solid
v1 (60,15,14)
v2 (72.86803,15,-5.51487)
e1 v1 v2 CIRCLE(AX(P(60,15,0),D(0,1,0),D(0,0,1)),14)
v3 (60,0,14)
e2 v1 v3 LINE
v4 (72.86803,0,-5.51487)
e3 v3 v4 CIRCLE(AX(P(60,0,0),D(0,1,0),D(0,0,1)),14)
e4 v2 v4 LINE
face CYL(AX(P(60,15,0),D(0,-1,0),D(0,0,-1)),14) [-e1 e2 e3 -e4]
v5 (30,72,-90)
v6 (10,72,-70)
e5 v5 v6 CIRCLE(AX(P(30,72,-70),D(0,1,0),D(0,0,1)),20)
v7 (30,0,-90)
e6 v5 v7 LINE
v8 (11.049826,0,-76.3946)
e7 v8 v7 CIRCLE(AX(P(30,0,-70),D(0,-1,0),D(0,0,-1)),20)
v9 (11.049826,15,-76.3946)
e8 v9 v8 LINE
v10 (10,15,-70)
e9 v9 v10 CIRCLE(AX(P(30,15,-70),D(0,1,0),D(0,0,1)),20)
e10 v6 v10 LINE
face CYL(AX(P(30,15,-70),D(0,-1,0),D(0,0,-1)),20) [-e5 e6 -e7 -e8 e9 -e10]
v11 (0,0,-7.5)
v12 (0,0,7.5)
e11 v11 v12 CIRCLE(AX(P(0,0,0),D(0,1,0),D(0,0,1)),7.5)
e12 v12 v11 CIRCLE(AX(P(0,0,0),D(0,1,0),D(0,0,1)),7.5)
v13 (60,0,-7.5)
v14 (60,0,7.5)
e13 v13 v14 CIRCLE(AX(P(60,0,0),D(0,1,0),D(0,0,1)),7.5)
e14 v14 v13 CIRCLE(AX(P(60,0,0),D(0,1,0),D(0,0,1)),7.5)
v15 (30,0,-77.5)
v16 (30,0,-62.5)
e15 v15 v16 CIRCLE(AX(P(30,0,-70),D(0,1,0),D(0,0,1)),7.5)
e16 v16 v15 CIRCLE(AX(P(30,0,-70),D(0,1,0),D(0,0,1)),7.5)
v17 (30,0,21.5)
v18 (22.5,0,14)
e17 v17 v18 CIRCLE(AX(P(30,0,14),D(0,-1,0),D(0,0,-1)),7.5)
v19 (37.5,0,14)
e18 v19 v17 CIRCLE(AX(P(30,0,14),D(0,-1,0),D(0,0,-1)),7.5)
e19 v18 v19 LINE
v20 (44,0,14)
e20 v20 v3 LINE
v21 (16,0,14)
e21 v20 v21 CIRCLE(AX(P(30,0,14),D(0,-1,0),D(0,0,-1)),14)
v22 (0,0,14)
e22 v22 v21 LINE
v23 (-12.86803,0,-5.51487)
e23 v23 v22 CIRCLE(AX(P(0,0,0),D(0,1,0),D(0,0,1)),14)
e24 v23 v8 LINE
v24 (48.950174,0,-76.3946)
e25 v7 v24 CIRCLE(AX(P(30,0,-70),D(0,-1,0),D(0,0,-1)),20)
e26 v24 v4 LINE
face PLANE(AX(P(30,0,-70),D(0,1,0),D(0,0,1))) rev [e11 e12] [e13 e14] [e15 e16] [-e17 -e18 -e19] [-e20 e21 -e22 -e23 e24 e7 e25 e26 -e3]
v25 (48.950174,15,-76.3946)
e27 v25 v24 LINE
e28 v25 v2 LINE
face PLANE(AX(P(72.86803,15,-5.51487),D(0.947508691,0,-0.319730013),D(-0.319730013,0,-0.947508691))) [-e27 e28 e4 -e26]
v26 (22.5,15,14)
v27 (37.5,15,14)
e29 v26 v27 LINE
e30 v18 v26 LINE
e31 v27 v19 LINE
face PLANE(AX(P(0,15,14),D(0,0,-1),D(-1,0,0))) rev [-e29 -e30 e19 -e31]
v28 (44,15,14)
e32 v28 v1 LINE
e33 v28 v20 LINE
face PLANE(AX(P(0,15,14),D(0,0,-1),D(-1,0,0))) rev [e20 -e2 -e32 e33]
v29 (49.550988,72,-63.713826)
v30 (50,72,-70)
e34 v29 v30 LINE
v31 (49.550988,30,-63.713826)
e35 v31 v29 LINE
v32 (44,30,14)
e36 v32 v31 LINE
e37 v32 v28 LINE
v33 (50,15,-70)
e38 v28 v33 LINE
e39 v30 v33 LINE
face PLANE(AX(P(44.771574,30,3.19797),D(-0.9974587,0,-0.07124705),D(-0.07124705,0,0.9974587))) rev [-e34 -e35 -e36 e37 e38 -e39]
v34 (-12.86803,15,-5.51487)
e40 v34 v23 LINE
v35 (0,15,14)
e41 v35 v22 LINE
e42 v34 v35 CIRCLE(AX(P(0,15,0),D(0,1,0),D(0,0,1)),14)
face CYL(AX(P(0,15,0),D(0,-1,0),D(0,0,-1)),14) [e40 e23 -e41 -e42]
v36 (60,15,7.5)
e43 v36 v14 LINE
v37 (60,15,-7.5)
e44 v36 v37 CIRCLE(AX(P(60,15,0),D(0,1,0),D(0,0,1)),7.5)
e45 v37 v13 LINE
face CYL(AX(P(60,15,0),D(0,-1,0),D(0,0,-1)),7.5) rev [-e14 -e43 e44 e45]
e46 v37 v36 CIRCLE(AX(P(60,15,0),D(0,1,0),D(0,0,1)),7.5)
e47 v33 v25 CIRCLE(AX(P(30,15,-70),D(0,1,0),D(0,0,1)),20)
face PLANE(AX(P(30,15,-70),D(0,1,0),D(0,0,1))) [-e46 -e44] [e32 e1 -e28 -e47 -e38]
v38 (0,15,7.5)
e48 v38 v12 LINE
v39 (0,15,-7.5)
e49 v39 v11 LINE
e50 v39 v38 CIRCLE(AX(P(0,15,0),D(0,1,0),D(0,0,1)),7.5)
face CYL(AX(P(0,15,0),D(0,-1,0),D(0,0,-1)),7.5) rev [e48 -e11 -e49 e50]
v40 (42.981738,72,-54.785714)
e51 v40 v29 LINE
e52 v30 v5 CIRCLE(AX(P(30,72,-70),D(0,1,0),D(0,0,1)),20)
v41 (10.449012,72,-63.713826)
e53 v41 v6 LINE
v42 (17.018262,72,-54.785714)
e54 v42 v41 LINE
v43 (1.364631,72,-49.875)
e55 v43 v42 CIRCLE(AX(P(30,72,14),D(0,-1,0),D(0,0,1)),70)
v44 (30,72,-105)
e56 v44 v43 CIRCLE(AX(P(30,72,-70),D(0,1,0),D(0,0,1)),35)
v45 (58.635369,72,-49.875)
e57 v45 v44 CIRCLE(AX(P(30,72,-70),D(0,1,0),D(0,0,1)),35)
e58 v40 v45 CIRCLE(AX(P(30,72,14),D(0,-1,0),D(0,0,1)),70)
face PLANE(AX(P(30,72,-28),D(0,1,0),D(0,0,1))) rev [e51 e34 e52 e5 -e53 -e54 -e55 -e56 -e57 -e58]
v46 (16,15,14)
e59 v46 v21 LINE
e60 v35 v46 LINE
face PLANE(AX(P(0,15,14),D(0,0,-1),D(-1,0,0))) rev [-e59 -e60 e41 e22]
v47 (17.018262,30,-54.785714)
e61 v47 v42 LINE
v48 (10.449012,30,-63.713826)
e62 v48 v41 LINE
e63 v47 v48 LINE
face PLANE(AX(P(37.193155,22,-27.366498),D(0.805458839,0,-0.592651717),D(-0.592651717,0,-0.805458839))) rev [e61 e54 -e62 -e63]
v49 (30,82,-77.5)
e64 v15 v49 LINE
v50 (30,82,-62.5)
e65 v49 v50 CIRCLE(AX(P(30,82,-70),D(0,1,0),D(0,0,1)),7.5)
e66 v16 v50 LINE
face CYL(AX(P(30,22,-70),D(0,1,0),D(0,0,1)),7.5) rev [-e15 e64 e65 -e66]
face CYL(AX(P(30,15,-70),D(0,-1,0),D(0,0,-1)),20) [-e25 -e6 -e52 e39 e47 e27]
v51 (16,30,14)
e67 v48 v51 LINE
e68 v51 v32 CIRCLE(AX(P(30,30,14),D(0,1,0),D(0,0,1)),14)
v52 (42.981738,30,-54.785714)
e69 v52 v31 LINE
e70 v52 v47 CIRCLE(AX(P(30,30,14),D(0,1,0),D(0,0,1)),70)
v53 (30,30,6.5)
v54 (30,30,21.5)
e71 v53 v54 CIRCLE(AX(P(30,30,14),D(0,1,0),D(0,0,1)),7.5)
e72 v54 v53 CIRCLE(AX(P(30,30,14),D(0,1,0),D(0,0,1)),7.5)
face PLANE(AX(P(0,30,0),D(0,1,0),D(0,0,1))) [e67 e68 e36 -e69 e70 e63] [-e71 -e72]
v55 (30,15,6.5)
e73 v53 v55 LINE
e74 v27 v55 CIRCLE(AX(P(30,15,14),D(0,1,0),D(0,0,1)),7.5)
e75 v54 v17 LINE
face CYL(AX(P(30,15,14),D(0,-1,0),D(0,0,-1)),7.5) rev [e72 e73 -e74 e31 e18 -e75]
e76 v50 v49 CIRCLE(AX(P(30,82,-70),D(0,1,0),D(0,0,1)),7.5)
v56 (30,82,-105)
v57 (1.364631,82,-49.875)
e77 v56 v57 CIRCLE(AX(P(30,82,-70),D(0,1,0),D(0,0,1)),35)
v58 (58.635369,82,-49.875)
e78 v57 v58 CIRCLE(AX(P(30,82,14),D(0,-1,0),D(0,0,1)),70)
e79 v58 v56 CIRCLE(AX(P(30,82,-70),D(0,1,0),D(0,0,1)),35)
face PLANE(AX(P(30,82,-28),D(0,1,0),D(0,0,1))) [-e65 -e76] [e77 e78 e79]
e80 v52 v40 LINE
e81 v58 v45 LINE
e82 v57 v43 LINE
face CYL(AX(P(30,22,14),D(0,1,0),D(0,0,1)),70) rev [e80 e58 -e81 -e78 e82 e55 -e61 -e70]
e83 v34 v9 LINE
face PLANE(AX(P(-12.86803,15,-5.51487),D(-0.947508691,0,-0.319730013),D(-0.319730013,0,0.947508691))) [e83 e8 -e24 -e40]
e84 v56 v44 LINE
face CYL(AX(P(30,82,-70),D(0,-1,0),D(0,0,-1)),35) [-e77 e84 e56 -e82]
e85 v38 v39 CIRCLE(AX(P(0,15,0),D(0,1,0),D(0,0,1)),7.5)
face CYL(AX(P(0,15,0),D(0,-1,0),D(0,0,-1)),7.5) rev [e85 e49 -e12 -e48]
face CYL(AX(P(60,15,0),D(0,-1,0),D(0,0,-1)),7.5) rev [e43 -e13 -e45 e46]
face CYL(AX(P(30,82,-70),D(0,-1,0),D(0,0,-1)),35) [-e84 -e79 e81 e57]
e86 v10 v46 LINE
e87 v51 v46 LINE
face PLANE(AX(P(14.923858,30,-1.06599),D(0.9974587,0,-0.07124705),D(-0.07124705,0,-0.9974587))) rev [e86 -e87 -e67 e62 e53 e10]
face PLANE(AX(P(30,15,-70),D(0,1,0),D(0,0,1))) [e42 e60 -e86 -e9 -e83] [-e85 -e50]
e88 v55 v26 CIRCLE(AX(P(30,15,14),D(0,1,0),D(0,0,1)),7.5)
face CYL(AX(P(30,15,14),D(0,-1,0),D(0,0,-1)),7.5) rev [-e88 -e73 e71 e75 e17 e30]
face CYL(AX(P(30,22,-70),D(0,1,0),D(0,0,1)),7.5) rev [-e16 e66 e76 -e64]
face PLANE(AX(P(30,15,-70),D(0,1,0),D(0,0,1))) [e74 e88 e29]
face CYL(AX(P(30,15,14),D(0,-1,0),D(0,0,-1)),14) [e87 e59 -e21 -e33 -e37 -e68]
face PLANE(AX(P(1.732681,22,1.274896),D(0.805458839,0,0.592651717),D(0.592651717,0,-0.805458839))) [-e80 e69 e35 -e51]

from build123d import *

# Parameters (mm, degrees)
BASE_PLATE_SKETCH_R  = 7.5
BASE_PLATE_DEPTH     = 15
UPRIGHT_WEB_SKETCH_R = 7.5
UPRIGHT_WEB_DEPTH    = 15
COLUMN_DEPTH         = 15
SWIVEL_START         = -50
SWIVEL_HEAD_SKETCH_R = 7.5
SWIVEL_HEAD_DEPTH    = 50
GUSSET_SKETCH_R      = 7.5
GUSSET_DEPTH         = 10
PIVOT_START          = -40
PIVOT_HOLE_SKETCH_R  = 7.5
PIVOT_HOLE_DEPTH     = 40


with BuildPart() as part:
    # Base Plate Sketch → Base Plate (new body)
    with BuildSketch(Plane(origin=(0, 0, 0), x_dir=(1, 0, 0), z_dir=(0, 1, 0))):
        with BuildLine():
            Line((17.13196958, 75.51487018), (-12.86803042, 5.51487018))
            ThreePointArc((-12.86803042, 5.51487018), (-11.687775291, -7.706874122), (0, -14))
            Line((0, -14), (60, -14))
            ThreePointArc((60, -14), (71.687775291, -7.706874122), (72.86803042, 5.51487018))
            Line((72.86803042, 5.51487018), (42.86803042, 75.51487018))
            ThreePointArc((42.86803042, 75.51487018), (30, 84), (17.13196958, 75.51487018))
        make_face()
        with Locations(Location((0, 0, 0), (0, 0, 270))):
            Circle(BASE_PLATE_SKETCH_R, mode=Mode.SUBTRACT)
        with Locations(Location((60, 0, 0), (0, 0, 270))):
            Circle(BASE_PLATE_SKETCH_R, mode=Mode.SUBTRACT)
        with Locations(Location((30, 70, 0), (0, 0, 270))):
            Circle(BASE_PLATE_SKETCH_R, mode=Mode.SUBTRACT)
    extrude(amount=BASE_PLATE_DEPTH)

    # Upright Web Sketch → Upright Web (add)
    with BuildSketch(Plane.XZ):
        with BuildLine():
            Line((-12.86803042, -5.51487018), (11.049826186, -76.394600254))
            ThreePointArc((11.049826186, -76.394600254), (30, -90), (48.950173814, -76.394600254))
            Line((48.950173814, -76.394600254), (72.86803042, -5.51487018))
            ThreePointArc((72.86803042, -5.51487018), (71.687775291, 7.706874122), (60, 14))
            Line((60, 14), (44, 14))
            ThreePointArc((44, 14), (30, 28), (16, 14))
            Line((16, 14), (0, 14))
            ThreePointArc((0, 14), (-11.687775291, 7.706874122), (-12.86803042, -5.51487018))
        make_face()
        with Locations((30, 14)):
            Circle(UPRIGHT_WEB_SKETCH_R, mode=Mode.SUBTRACT)
        with Locations(Location((0, 0, 0), (0, 0, 90))):
            Circle(UPRIGHT_WEB_SKETCH_R, mode=Mode.SUBTRACT)
        with Locations(Location((60, 0, 0), (0, 0, 90))):
            Circle(UPRIGHT_WEB_SKETCH_R, mode=Mode.SUBTRACT)
    extrude(amount=-UPRIGHT_WEB_DEPTH)

    # Column Sketch → Column (add)
    with BuildSketch(Plane(origin=(0, 15, 0), x_dir=(1, 0, 0), z_dir=(0, 1, 0))):
        with BuildLine():
            ThreePointArc((11.049826186, 76.394600254), (10.264201609, 73.240102137), (10, 70))
            Line((10, 70), (10.203045685, 67.157360406))
            Line((10.203045685, 67.157360406), (16, -14))
            ThreePointArc((16, -14), (30, -28), (44, -14))
            Line((44, -14), (49.796954315, 67.157360406))
            Line((49.796954315, 67.157360406), (50, 70))
            ThreePointArc((50, 70), (49.735798391, 73.240102137), (48.950173814, 76.394600254))
            ThreePointArc((48.950173814, 76.394600254), (30, 90), (11.049826186, 76.394600254))
        make_face()
        with BuildLine():
            ThreePointArc((37.5, -14), (30, -21.5), (22.5, -14))
            ThreePointArc((22.5, -14), (30, -6.5), (37.5, -14))
        make_face(mode=Mode.SUBTRACT)
    extrude(amount=COLUMN_DEPTH)

    # Swivel Head Sketch → Swivel Head (add)
    with BuildSketch(Plane(origin=(0, 72, 0), x_dir=(1, 0, 0), z_dir=(0, 1, 0)).offset(SWIVEL_START)):
        with BuildLine():
            ThreePointArc((17.018262435, 54.785714286), (30, 56), (42.981737565, 54.785714286))
            Line((42.981737565, 54.785714286), (49.550987537, 63.713825524))
            Line((49.550987537, 63.713825524), (49.796954315, 67.157360406))
            Line((49.796954315, 67.157360406), (50, 70))
            ThreePointArc((50, 70), (30, 90), (10, 70))
            Line((10, 70), (10.203045685, 67.157360406))
            Line((10.203045685, 67.157360406), (10.449012463, 63.713825524))
            Line((10.449012463, 63.713825524), (17.018262435, 54.785714286))
        make_face()
        with Locations(Location((30, 70, 0), (0, 0, 270))):
            Circle(SWIVEL_HEAD_SKETCH_R, mode=Mode.SUBTRACT)
    extrude(amount=SWIVEL_HEAD_DEPTH)

    # Gusset Sketch → Gusset (add)
    with BuildSketch(Plane(origin=(0, 72, 0), x_dir=(1, 0, 0), z_dir=(0, 1, 0))):
        with BuildLine():
            ThreePointArc((58.635369301, 49.875), (30, 105), (1.364630699, 49.875))
            ThreePointArc((1.364630699, 49.875), (30, 56), (58.635369301, 49.875))
        make_face()
        with Locations(Location((30, 70, 0), (0, 0, 270))):
            Circle(GUSSET_SKETCH_R, mode=Mode.SUBTRACT)
    extrude(amount=GUSSET_DEPTH)

    # Pivot Hole Sketch → Pivot Hole (cut)
    with BuildSketch(Plane(origin=(0, 30, 0), x_dir=(1, 0, 0), z_dir=(0, 1, 0)).offset(PIVOT_START)):
        with Locations(Location((30, 70, 0), (0, 0, 270))):
            Circle(PIVOT_HOLE_SKETCH_R)
    extrude(amount=PIVOT_HOLE_DEPTH, mode=Mode.SUBTRACT)


solid = part.part
